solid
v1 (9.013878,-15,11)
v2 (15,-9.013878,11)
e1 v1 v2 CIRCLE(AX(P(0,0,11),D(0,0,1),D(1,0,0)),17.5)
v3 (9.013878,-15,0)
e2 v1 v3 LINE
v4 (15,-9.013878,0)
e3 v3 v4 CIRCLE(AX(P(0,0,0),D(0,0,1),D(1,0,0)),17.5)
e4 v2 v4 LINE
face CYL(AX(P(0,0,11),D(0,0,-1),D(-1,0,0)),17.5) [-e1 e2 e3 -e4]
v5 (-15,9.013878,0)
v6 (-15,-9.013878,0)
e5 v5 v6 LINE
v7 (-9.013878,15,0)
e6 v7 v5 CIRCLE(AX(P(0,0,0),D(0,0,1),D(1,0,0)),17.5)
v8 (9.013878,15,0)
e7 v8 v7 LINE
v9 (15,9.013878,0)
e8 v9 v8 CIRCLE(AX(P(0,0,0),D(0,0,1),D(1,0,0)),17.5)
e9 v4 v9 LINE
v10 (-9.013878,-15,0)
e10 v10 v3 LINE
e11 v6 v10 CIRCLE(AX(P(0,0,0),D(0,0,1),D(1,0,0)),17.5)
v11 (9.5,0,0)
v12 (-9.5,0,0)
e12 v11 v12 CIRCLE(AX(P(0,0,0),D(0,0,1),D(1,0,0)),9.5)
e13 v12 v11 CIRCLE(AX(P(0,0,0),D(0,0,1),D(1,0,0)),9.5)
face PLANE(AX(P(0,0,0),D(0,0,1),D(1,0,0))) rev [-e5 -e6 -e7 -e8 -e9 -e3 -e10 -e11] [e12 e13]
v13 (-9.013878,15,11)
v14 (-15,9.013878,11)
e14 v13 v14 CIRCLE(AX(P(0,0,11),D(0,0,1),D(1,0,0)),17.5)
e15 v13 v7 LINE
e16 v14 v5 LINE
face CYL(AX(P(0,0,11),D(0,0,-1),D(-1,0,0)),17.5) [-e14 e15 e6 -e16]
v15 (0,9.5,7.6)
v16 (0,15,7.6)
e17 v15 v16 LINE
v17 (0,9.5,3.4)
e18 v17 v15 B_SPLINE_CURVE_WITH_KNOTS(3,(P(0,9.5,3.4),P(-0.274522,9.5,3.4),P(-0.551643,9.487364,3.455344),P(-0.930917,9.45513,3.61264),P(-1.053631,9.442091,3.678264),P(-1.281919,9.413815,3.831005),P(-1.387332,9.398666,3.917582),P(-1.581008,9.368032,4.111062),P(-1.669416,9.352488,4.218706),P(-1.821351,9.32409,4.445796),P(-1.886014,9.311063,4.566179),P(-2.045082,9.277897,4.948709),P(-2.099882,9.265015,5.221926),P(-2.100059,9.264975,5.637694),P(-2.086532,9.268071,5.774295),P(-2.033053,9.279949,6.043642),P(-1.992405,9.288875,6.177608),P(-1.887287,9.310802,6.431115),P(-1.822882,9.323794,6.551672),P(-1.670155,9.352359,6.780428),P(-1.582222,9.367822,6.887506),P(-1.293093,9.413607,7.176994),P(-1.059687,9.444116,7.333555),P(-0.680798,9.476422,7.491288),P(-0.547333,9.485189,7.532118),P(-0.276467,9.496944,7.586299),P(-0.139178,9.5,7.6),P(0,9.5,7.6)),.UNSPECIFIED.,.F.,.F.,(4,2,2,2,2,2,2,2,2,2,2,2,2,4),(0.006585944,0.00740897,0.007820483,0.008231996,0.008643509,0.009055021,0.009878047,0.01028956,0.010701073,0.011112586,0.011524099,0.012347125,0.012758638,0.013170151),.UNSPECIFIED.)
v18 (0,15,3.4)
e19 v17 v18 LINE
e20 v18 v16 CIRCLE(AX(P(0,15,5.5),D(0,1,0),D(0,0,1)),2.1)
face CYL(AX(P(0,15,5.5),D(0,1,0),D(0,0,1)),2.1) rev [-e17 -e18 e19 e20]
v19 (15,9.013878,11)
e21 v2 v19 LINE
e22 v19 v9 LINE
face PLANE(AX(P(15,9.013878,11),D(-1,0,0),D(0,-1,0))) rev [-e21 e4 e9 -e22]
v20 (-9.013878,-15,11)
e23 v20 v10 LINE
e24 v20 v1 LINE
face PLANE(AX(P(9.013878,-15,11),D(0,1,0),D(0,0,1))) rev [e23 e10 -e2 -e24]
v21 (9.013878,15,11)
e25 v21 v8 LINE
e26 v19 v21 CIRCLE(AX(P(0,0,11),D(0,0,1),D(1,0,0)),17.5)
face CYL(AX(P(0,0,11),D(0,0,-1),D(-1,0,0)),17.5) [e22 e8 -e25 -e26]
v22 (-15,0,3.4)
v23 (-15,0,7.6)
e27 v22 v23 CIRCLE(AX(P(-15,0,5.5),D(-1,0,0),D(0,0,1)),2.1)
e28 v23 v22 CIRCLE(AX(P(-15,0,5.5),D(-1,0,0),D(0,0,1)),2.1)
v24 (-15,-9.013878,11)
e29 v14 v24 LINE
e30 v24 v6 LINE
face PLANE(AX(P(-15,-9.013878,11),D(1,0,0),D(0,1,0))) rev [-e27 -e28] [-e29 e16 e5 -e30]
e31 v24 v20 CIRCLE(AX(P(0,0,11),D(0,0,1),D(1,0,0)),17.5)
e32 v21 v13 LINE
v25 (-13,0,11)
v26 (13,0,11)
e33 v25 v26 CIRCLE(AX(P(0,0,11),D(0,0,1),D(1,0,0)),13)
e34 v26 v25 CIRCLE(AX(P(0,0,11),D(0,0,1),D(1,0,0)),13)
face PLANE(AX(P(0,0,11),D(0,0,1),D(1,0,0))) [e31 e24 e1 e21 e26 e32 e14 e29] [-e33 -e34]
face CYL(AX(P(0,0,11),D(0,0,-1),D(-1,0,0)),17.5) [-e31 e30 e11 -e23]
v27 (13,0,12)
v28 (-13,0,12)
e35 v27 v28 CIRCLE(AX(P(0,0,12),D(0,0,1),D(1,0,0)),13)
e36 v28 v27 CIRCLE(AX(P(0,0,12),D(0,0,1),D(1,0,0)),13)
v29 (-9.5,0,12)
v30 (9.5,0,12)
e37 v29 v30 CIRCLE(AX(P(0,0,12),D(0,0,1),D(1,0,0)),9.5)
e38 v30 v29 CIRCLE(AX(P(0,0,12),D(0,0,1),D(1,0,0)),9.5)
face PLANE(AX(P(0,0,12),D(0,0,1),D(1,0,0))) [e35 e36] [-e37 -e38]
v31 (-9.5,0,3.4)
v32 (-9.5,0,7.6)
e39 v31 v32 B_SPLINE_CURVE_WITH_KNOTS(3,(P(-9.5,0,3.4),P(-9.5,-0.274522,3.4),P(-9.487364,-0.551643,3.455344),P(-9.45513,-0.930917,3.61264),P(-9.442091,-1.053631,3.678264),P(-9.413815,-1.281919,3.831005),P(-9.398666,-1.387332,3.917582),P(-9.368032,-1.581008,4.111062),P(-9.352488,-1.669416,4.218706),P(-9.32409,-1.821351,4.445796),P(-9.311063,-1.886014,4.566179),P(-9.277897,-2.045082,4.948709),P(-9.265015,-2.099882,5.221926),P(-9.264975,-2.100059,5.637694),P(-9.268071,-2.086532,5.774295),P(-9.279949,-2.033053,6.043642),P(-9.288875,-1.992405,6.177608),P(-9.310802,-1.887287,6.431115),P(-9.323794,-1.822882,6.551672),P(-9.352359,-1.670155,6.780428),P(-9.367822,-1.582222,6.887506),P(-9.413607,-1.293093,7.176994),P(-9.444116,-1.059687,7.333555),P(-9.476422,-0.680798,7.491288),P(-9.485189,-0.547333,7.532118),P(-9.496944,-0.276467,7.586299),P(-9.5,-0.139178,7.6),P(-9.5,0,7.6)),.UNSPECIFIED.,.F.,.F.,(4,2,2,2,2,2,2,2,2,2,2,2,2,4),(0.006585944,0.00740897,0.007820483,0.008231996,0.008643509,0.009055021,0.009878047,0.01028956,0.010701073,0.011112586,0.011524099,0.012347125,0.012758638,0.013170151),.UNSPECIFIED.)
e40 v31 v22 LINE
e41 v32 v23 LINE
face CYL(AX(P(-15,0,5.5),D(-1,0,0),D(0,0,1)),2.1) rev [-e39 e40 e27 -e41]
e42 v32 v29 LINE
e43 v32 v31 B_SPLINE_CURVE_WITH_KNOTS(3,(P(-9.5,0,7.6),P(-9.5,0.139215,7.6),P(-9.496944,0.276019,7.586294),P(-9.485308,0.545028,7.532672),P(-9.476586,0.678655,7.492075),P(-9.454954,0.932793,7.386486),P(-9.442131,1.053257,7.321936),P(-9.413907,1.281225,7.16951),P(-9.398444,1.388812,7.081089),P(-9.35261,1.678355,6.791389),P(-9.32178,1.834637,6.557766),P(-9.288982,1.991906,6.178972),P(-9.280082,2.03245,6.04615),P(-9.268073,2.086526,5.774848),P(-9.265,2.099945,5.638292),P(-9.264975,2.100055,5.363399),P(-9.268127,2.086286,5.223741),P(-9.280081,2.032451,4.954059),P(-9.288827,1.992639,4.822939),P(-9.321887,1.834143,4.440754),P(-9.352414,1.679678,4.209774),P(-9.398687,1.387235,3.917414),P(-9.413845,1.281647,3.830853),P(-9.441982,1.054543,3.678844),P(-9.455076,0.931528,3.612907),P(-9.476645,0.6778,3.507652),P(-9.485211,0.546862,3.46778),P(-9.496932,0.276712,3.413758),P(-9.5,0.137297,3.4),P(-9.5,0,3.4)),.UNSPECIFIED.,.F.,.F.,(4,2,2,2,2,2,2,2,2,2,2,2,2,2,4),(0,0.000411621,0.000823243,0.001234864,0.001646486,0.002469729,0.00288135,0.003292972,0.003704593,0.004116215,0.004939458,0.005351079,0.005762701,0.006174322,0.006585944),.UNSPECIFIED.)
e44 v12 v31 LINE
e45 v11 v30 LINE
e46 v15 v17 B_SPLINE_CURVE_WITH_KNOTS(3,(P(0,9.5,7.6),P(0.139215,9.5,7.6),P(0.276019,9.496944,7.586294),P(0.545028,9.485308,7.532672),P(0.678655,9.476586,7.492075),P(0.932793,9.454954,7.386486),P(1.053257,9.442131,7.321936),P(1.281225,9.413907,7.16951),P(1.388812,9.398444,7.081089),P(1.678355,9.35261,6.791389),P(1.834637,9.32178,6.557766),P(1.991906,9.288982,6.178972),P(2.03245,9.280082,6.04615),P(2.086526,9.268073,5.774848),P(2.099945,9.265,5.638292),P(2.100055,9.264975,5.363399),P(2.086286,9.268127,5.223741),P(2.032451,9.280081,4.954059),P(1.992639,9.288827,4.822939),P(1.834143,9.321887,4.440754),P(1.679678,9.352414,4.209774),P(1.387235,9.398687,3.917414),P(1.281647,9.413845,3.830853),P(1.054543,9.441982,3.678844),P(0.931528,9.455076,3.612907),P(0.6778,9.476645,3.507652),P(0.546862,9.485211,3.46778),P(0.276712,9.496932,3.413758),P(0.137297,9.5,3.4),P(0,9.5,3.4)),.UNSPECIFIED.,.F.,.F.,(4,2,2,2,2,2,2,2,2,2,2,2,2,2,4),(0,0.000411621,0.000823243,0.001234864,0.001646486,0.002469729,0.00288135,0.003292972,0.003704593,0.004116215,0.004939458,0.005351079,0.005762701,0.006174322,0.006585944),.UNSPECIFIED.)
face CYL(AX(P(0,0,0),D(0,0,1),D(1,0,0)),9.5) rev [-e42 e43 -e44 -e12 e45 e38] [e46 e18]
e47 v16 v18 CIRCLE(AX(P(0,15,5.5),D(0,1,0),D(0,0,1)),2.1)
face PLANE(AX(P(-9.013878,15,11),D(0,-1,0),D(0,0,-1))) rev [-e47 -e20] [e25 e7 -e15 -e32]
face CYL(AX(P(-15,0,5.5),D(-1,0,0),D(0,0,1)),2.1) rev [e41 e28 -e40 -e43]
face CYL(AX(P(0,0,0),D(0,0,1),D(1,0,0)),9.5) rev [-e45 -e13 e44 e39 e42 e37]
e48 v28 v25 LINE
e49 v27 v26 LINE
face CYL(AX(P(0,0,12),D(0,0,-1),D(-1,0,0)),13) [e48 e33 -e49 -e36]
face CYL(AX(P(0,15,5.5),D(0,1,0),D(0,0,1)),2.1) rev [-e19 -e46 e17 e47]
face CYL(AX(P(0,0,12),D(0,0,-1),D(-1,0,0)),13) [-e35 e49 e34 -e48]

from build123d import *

# Parameters (mm, degrees)
BOSS_EXTRUDE1_DEPTH    = 11
SKETCH2_R              = 13
BOSS_EXTRUDE2_DEPTH    = 1
SKETCH3_R              = 9.5
CUT_EXTRUDE1_DEPTH     = 25.372115214
M5_TAPPED_HOLE1_REACH  = 37.623
M5_TAPPED_HOLE1_BORE_R = 2.1
M5_TAPPED_HOLE2_REACH  = 37.623
M5_TAPPED_HOLE2_BORE_R = 2.1


with BuildPart() as part:
    # Sketch1 → Boss-Extrude1 (new body)
    with BuildSketch(Plane.XY):
        with BuildLine():
            Line((-9.013878189, 15), (9.013878189, 15))
            ThreePointArc((9.013878189, 15), (12.374368671, 12.374368671), (15, 9.013878189))
            Line((15, 9.013878189), (15, -9.013878189))
            ThreePointArc((15, -9.013878189), (12.374368671, -12.374368671), (9.013878189, -15))
            Line((9.013878189, -15), (-9.013878189, -15))
            ThreePointArc((-9.013878189, -15), (-12.374368671, -12.374368671), (-15, -9.013878189))
            Line((-15, -9.013878189), (-15, 9.013878189))
            ThreePointArc((-15, 9.013878189), (-12.374368671, 12.374368671), (-9.013878189, 15))
        make_face()
    extrude(amount=BOSS_EXTRUDE1_DEPTH)

    # Sketch2 → Boss-Extrude2 (add)
    with BuildSketch(Plane.XY.offset(11)):
        Circle(SKETCH2_R)
    extrude(amount=BOSS_EXTRUDE2_DEPTH)

    # Sketch3 → Cut-Extrude1 (cut, through all)
    with BuildSketch(Plane.XY.offset(12)):
        Circle(SKETCH3_R)
    extrude(amount=-CUT_EXTRUDE1_DEPTH, mode=Mode.SUBTRACT)

    # M5 Tapped Hole1 bore → M5 Tapped Hole1 (cut, up to next)
    with BuildSketch(Plane.ZY.offset(15), mode=Mode.PRIVATE) as m5_tapped_hole1_sk1:
        with Locations((5.5, 0)):
            Circle(M5_TAPPED_HOLE1_BORE_R)
    m5_tapped_hole1_tool1 = extrude(m5_tapped_hole1_sk1.sketch, amount=-M5_TAPPED_HOLE1_REACH, mode=Mode.PRIVATE) & part.part
    add(m5_tapped_hole1_tool1.solids().sort_by_distance((-15, 0, 5.5))[0], mode=Mode.SUBTRACT)

    # M5 Tapped Hole2 bore → M5 Tapped Hole2 (cut, up to next)
    with BuildSketch(Plane(origin=(0, 15, 0), x_dir=(-1, 0, 0), z_dir=(0, 1, 0)), mode=Mode.PRIVATE) as m5_tapped_hole2_sk1:
        with Locations((0, 5.5)):
            Circle(M5_TAPPED_HOLE2_BORE_R)
    m5_tapped_hole2_tool1 = extrude(m5_tapped_hole2_sk1.sketch, amount=-M5_TAPPED_HOLE2_REACH, mode=Mode.PRIVATE) & part.part
    add(m5_tapped_hole2_tool1.solids().sort_by_distance((0, 15, 5.5))[0], mode=Mode.SUBTRACT)


solid = part.part
